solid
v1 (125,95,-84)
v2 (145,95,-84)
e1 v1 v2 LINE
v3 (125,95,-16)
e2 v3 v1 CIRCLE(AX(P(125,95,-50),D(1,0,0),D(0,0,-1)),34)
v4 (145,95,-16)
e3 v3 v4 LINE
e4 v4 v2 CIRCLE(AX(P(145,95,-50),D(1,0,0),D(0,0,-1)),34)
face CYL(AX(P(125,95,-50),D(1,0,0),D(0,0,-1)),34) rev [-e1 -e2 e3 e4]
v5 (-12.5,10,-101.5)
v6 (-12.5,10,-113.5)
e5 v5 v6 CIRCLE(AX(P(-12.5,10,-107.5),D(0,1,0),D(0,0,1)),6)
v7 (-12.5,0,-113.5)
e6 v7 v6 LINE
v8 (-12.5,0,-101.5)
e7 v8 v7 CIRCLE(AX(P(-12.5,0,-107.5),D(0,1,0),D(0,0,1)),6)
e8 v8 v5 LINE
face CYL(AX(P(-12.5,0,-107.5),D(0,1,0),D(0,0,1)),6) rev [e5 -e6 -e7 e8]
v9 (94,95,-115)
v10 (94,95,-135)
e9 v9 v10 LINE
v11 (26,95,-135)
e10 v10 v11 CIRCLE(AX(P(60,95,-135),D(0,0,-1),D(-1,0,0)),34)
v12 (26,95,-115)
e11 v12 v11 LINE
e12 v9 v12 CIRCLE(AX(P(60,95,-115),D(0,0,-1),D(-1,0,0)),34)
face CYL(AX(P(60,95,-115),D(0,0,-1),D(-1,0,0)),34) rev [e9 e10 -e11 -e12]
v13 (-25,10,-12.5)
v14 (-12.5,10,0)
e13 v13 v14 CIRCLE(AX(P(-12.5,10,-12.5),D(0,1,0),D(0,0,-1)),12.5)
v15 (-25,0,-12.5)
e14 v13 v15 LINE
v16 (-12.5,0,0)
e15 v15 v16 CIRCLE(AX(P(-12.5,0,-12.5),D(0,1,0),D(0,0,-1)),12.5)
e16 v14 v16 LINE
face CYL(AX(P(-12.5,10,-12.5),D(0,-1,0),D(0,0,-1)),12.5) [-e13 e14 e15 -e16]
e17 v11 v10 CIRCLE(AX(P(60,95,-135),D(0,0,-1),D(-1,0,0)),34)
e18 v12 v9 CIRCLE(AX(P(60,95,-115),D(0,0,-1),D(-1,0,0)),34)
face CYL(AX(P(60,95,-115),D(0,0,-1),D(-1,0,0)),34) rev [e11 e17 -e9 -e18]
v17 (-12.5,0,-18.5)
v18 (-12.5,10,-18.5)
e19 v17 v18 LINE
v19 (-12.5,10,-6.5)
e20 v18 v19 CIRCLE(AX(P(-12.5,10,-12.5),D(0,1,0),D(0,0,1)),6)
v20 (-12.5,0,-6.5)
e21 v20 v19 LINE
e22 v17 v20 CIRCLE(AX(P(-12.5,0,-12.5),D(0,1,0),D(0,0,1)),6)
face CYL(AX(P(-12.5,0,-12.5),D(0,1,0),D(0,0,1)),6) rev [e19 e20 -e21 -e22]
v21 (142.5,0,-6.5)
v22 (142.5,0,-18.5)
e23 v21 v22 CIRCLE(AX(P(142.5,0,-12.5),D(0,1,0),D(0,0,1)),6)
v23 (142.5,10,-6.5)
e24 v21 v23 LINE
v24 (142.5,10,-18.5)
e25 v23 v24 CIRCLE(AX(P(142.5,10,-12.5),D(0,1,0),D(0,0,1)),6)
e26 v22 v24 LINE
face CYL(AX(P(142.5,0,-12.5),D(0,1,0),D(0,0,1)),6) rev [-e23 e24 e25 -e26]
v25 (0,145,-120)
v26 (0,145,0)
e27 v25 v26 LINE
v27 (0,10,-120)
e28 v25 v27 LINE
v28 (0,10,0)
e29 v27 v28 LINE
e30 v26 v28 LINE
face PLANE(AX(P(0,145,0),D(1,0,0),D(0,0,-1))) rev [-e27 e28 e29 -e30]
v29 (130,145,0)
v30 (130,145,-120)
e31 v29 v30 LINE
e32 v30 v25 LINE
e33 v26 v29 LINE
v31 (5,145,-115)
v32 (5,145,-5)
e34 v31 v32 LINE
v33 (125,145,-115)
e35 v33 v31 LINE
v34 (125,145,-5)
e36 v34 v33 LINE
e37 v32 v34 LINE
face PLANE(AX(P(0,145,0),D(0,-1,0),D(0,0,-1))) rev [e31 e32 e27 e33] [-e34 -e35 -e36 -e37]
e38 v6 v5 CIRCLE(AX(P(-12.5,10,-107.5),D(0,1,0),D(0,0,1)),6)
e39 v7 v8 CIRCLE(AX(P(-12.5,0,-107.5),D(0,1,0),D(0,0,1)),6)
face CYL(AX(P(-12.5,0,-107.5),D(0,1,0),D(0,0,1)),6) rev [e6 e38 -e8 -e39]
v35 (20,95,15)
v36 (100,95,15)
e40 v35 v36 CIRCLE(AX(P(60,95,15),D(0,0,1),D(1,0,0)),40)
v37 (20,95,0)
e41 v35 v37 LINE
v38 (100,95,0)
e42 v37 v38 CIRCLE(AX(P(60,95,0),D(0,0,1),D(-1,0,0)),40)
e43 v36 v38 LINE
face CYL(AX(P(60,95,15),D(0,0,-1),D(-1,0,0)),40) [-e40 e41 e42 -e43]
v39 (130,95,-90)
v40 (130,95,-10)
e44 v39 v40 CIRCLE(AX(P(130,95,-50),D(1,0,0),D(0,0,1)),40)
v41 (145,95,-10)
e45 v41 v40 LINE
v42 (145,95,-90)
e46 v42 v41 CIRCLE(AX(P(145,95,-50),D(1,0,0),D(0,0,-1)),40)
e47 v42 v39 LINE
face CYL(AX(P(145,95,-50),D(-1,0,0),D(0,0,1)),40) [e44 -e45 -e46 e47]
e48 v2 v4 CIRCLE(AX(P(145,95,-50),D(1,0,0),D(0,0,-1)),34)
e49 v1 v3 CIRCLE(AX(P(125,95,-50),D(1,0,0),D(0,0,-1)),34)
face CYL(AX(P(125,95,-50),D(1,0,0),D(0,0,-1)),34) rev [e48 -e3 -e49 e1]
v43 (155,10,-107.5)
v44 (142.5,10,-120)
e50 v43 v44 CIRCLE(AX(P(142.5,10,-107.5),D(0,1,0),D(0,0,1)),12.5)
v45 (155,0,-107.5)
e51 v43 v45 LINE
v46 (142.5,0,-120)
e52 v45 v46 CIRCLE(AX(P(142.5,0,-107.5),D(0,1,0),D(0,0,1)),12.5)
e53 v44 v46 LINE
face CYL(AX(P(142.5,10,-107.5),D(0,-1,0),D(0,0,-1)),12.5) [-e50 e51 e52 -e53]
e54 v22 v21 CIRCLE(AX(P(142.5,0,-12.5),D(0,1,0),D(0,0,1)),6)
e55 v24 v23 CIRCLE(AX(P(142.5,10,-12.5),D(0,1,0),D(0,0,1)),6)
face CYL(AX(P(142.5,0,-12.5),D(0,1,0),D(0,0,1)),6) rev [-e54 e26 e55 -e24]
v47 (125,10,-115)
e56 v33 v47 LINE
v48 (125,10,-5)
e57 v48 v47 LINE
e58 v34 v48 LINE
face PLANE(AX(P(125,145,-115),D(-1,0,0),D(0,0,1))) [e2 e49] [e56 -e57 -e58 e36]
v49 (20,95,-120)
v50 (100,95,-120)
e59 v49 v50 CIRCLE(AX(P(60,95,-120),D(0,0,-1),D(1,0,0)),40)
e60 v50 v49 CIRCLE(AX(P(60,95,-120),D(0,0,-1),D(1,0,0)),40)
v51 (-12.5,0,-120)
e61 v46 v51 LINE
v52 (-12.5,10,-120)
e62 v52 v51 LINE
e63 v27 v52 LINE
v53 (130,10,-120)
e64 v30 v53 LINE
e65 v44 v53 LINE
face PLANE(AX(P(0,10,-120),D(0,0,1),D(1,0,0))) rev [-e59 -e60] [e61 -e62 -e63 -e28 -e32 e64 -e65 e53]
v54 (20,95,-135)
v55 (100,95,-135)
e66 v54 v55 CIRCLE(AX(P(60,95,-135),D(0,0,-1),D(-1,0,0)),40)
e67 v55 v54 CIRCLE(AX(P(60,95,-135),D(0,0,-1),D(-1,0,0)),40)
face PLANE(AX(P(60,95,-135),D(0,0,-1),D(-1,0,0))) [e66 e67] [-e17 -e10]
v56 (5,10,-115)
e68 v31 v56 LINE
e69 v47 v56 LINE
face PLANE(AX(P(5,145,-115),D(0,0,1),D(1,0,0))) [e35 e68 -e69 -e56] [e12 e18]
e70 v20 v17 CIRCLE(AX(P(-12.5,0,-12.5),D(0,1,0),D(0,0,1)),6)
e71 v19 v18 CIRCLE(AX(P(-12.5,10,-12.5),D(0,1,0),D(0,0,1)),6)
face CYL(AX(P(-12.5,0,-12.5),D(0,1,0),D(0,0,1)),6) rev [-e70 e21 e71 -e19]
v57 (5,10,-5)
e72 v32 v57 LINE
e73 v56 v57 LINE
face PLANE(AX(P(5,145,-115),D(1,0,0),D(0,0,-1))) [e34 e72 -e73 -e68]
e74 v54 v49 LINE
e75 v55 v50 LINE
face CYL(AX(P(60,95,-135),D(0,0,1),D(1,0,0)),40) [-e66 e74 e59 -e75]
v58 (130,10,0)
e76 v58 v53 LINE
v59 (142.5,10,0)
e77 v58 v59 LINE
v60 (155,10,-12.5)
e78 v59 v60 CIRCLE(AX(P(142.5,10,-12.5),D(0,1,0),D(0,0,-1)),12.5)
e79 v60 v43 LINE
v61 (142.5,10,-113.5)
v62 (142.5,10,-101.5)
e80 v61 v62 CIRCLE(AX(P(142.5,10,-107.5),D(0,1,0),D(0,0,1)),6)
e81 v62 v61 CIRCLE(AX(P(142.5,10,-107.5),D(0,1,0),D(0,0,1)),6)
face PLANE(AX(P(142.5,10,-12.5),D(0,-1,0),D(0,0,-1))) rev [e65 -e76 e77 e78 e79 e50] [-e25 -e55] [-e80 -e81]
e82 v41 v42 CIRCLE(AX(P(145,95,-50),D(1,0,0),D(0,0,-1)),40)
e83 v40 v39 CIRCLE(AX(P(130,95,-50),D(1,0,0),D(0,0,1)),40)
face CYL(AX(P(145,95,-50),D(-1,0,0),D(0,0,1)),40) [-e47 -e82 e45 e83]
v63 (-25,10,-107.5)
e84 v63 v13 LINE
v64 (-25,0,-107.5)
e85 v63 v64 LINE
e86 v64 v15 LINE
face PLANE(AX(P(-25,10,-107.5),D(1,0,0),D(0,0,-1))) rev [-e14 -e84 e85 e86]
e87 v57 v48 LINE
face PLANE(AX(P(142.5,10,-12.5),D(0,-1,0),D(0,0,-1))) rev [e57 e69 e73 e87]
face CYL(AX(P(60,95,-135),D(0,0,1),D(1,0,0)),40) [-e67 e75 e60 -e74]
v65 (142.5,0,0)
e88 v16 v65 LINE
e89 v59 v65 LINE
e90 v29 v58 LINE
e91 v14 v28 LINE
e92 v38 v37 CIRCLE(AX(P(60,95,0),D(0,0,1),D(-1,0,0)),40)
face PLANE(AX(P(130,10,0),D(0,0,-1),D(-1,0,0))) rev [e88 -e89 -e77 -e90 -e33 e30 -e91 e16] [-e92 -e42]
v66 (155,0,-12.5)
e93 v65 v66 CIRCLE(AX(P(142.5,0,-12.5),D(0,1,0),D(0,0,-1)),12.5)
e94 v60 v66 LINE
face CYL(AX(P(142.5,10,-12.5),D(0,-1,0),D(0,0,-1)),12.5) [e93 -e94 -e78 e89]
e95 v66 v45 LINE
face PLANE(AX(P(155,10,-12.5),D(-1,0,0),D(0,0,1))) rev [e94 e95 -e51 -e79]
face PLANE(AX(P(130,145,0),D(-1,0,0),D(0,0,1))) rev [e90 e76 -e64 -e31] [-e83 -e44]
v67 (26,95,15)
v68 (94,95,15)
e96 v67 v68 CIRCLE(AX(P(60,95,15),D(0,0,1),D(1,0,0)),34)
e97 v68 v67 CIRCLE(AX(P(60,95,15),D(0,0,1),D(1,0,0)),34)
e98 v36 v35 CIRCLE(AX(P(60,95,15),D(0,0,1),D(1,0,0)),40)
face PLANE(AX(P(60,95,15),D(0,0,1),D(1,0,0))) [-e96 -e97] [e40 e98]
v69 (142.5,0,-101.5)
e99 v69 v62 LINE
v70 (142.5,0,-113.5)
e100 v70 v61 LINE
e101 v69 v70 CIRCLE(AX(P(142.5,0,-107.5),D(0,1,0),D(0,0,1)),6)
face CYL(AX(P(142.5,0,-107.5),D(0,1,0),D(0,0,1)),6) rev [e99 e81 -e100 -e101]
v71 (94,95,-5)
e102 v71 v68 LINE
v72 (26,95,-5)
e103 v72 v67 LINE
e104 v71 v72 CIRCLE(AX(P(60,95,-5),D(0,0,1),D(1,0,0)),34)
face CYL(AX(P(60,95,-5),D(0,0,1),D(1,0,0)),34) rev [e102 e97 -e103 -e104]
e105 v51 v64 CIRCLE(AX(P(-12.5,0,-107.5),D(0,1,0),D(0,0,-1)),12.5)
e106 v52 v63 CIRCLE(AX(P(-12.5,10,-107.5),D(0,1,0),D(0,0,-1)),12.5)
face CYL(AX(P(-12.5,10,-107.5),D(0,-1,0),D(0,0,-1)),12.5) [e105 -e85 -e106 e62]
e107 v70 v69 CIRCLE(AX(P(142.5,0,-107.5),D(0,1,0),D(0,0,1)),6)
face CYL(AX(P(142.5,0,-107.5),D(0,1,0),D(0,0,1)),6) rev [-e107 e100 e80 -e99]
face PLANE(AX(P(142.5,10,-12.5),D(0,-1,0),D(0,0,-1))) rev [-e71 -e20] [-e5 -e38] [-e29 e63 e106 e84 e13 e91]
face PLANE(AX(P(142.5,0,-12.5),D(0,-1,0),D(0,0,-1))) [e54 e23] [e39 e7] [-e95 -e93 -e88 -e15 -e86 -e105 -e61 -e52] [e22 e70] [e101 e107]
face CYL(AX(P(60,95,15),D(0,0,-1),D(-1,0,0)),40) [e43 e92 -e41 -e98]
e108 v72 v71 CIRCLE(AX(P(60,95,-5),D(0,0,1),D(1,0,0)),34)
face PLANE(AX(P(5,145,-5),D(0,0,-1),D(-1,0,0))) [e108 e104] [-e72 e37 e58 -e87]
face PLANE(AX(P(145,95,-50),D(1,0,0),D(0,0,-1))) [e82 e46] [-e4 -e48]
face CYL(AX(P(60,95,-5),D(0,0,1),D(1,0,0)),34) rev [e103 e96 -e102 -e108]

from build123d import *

# Parameters (mm, degrees)
EXTRUDE_1_DEPTH     = 10
SKETCH_2_R          = 6
CUT_EXTRUDE_1_DEPTH = 197.277864264
SKETCH_3_W          = 130
SKETCH_3_H          = 120
SKETCH_3_W_2        = 120
SKETCH_3_H_2        = 110
EXTRUDE_4_DEPTH     = 135
SKETCH_4_R          = 40
EXTRUDE_5_DEPTH     = 15
SKETCH_6_R          = 34
CUT_EXTRUDE_2_DEPTH = 20
SKETCH_7_R          = 40
EXTRUDE_6_DEPTH     = 15
SKETCH_8_R          = 34
CUT_EXTRUDE_3_DEPTH = 20
EXTRUDE_START       = 15
SKETCH_9_R          = 40
EXTRUDE_7_DEPTH     = 15
CUT_EXTRUDE_START   = -20
SKETCH_10_R         = 34
CUT_EXTRUDE_4_DEPTH = 20


with BuildPart() as part:
    # 草图1 → 凸台-拉伸1 (new body)
    with BuildSketch(Plane(origin=(0, 0, 0), x_dir=(1, 0, 0), z_dir=(0, 1, 0))):
        with BuildLine():
            Line((0, 120), (-12.5, 120))
            ThreePointArc((-12.5, 120), (-21.338834765, 116.338834765), (-25, 107.5))
            Line((-25, 107.5), (-25, 12.5))
            ThreePointArc((-25, 12.5), (-21.338834765, 3.661165235), (-12.5, 0))
            Line((-12.5, 0), (0, 0))
            Line((0, 0), (130, 0))
            Line((130, 0), (142.5, 0))
            ThreePointArc((142.5, 0), (151.338834765, 3.661165235), (155, 12.5))
            Line((155, 12.5), (155, 107.5))
            ThreePointArc((155, 107.5), (151.338834765, 116.338834765), (142.5, 120))
            Line((142.5, 120), (130, 120))
            Line((130, 120), (0, 120))
        make_face()
    extrude(amount=EXTRUDE_1_DEPTH)

    # 草图2 → 切除-拉伸1 (cut, through all)
    with BuildSketch(Plane(origin=(0, 10, 0), x_dir=(1, 0, 0), z_dir=(0, 1, 0))):
        with Locations(Location((-12.5, 107.5, 0), (0, 0, 270))):
            Circle(SKETCH_2_R)
        with Locations(Location((142.5, 107.5, 0), (0, 0, 270))):
            Circle(SKETCH_2_R)
        with Locations(Location((142.5, 12.5, 0), (0, 0, 270))):
            Circle(SKETCH_2_R)
        with Locations(Location((-12.5, 12.5, 0), (0, 0, 270))):
            Circle(SKETCH_2_R)
    extrude(amount=-CUT_EXTRUDE_1_DEPTH, mode=Mode.SUBTRACT)

    # 草图3 → 凸台-拉伸4 (add)
    with BuildSketch(Plane(origin=(0, 10, 0), x_dir=(1, 0, 0), z_dir=(0, 1, 0))):
        with Locations((65, 60)):
            Rectangle(SKETCH_3_W, SKETCH_3_H)
        with Locations((65, 60)):
            Rectangle(SKETCH_3_W_2, SKETCH_3_H_2, mode=Mode.SUBTRACT)
    extrude(amount=EXTRUDE_4_DEPTH)

    # 草图4 → 凸台-拉伸5 (add)
    with BuildSketch(Plane.XY):
        with Locations(Location((60, 95, 0), (0, 0, 180))):
            Circle(SKETCH_4_R)
    extrude(amount=EXTRUDE_5_DEPTH)

    # 草图6 → 切除-拉伸2 (cut)
    with BuildSketch(Plane.XY.offset(15)):
        with Locations((60, 95)):
            Circle(SKETCH_6_R)
    extrude(amount=-CUT_EXTRUDE_2_DEPTH, mode=Mode.SUBTRACT)

    # 草图7 → 凸台-拉伸6 (add)
    with BuildSketch(Plane(origin=(130, 0, 0), x_dir=(0, 0, -1), z_dir=(1, 0, 0))):
        with Locations(Location((50, 95, 0), (0, 0, 180))):
            Circle(SKETCH_7_R)
    extrude(amount=EXTRUDE_6_DEPTH)

    # 草图8 → 切除-拉伸3 (cut)
    with BuildSketch(Plane(origin=(145, 0, 0), x_dir=(0, 0, -1), z_dir=(1, 0, 0))):
        with Locations((50, 95)):
            Circle(SKETCH_8_R)
    extrude(amount=-CUT_EXTRUDE_3_DEPTH, mode=Mode.SUBTRACT)

    # 草图9 → 凸台-拉伸7 (add)
    with BuildSketch(Plane(origin=(0, 0, -120), x_dir=(-1, 0, 0), z_dir=(0, 0, -1)).offset(EXTRUDE_START)):
        with Locations((-60, 95)):
            Circle(SKETCH_9_R)
    extrude(amount=-EXTRUDE_7_DEPTH)

    # 草图10 → 切除-拉伸4 (cut)
    with BuildSketch(Plane(origin=(0, 0, -135), x_dir=(-1, 0, 0), z_dir=(0, 0, -1)).offset(CUT_EXTRUDE_START)):
        with Locations(Location((-60, 95, 0), (0, 0, 180))):
            Circle(SKETCH_10_R)
    extrude(amount=CUT_EXTRUDE_4_DEPTH, mode=Mode.SUBTRACT)


solid = part.part
